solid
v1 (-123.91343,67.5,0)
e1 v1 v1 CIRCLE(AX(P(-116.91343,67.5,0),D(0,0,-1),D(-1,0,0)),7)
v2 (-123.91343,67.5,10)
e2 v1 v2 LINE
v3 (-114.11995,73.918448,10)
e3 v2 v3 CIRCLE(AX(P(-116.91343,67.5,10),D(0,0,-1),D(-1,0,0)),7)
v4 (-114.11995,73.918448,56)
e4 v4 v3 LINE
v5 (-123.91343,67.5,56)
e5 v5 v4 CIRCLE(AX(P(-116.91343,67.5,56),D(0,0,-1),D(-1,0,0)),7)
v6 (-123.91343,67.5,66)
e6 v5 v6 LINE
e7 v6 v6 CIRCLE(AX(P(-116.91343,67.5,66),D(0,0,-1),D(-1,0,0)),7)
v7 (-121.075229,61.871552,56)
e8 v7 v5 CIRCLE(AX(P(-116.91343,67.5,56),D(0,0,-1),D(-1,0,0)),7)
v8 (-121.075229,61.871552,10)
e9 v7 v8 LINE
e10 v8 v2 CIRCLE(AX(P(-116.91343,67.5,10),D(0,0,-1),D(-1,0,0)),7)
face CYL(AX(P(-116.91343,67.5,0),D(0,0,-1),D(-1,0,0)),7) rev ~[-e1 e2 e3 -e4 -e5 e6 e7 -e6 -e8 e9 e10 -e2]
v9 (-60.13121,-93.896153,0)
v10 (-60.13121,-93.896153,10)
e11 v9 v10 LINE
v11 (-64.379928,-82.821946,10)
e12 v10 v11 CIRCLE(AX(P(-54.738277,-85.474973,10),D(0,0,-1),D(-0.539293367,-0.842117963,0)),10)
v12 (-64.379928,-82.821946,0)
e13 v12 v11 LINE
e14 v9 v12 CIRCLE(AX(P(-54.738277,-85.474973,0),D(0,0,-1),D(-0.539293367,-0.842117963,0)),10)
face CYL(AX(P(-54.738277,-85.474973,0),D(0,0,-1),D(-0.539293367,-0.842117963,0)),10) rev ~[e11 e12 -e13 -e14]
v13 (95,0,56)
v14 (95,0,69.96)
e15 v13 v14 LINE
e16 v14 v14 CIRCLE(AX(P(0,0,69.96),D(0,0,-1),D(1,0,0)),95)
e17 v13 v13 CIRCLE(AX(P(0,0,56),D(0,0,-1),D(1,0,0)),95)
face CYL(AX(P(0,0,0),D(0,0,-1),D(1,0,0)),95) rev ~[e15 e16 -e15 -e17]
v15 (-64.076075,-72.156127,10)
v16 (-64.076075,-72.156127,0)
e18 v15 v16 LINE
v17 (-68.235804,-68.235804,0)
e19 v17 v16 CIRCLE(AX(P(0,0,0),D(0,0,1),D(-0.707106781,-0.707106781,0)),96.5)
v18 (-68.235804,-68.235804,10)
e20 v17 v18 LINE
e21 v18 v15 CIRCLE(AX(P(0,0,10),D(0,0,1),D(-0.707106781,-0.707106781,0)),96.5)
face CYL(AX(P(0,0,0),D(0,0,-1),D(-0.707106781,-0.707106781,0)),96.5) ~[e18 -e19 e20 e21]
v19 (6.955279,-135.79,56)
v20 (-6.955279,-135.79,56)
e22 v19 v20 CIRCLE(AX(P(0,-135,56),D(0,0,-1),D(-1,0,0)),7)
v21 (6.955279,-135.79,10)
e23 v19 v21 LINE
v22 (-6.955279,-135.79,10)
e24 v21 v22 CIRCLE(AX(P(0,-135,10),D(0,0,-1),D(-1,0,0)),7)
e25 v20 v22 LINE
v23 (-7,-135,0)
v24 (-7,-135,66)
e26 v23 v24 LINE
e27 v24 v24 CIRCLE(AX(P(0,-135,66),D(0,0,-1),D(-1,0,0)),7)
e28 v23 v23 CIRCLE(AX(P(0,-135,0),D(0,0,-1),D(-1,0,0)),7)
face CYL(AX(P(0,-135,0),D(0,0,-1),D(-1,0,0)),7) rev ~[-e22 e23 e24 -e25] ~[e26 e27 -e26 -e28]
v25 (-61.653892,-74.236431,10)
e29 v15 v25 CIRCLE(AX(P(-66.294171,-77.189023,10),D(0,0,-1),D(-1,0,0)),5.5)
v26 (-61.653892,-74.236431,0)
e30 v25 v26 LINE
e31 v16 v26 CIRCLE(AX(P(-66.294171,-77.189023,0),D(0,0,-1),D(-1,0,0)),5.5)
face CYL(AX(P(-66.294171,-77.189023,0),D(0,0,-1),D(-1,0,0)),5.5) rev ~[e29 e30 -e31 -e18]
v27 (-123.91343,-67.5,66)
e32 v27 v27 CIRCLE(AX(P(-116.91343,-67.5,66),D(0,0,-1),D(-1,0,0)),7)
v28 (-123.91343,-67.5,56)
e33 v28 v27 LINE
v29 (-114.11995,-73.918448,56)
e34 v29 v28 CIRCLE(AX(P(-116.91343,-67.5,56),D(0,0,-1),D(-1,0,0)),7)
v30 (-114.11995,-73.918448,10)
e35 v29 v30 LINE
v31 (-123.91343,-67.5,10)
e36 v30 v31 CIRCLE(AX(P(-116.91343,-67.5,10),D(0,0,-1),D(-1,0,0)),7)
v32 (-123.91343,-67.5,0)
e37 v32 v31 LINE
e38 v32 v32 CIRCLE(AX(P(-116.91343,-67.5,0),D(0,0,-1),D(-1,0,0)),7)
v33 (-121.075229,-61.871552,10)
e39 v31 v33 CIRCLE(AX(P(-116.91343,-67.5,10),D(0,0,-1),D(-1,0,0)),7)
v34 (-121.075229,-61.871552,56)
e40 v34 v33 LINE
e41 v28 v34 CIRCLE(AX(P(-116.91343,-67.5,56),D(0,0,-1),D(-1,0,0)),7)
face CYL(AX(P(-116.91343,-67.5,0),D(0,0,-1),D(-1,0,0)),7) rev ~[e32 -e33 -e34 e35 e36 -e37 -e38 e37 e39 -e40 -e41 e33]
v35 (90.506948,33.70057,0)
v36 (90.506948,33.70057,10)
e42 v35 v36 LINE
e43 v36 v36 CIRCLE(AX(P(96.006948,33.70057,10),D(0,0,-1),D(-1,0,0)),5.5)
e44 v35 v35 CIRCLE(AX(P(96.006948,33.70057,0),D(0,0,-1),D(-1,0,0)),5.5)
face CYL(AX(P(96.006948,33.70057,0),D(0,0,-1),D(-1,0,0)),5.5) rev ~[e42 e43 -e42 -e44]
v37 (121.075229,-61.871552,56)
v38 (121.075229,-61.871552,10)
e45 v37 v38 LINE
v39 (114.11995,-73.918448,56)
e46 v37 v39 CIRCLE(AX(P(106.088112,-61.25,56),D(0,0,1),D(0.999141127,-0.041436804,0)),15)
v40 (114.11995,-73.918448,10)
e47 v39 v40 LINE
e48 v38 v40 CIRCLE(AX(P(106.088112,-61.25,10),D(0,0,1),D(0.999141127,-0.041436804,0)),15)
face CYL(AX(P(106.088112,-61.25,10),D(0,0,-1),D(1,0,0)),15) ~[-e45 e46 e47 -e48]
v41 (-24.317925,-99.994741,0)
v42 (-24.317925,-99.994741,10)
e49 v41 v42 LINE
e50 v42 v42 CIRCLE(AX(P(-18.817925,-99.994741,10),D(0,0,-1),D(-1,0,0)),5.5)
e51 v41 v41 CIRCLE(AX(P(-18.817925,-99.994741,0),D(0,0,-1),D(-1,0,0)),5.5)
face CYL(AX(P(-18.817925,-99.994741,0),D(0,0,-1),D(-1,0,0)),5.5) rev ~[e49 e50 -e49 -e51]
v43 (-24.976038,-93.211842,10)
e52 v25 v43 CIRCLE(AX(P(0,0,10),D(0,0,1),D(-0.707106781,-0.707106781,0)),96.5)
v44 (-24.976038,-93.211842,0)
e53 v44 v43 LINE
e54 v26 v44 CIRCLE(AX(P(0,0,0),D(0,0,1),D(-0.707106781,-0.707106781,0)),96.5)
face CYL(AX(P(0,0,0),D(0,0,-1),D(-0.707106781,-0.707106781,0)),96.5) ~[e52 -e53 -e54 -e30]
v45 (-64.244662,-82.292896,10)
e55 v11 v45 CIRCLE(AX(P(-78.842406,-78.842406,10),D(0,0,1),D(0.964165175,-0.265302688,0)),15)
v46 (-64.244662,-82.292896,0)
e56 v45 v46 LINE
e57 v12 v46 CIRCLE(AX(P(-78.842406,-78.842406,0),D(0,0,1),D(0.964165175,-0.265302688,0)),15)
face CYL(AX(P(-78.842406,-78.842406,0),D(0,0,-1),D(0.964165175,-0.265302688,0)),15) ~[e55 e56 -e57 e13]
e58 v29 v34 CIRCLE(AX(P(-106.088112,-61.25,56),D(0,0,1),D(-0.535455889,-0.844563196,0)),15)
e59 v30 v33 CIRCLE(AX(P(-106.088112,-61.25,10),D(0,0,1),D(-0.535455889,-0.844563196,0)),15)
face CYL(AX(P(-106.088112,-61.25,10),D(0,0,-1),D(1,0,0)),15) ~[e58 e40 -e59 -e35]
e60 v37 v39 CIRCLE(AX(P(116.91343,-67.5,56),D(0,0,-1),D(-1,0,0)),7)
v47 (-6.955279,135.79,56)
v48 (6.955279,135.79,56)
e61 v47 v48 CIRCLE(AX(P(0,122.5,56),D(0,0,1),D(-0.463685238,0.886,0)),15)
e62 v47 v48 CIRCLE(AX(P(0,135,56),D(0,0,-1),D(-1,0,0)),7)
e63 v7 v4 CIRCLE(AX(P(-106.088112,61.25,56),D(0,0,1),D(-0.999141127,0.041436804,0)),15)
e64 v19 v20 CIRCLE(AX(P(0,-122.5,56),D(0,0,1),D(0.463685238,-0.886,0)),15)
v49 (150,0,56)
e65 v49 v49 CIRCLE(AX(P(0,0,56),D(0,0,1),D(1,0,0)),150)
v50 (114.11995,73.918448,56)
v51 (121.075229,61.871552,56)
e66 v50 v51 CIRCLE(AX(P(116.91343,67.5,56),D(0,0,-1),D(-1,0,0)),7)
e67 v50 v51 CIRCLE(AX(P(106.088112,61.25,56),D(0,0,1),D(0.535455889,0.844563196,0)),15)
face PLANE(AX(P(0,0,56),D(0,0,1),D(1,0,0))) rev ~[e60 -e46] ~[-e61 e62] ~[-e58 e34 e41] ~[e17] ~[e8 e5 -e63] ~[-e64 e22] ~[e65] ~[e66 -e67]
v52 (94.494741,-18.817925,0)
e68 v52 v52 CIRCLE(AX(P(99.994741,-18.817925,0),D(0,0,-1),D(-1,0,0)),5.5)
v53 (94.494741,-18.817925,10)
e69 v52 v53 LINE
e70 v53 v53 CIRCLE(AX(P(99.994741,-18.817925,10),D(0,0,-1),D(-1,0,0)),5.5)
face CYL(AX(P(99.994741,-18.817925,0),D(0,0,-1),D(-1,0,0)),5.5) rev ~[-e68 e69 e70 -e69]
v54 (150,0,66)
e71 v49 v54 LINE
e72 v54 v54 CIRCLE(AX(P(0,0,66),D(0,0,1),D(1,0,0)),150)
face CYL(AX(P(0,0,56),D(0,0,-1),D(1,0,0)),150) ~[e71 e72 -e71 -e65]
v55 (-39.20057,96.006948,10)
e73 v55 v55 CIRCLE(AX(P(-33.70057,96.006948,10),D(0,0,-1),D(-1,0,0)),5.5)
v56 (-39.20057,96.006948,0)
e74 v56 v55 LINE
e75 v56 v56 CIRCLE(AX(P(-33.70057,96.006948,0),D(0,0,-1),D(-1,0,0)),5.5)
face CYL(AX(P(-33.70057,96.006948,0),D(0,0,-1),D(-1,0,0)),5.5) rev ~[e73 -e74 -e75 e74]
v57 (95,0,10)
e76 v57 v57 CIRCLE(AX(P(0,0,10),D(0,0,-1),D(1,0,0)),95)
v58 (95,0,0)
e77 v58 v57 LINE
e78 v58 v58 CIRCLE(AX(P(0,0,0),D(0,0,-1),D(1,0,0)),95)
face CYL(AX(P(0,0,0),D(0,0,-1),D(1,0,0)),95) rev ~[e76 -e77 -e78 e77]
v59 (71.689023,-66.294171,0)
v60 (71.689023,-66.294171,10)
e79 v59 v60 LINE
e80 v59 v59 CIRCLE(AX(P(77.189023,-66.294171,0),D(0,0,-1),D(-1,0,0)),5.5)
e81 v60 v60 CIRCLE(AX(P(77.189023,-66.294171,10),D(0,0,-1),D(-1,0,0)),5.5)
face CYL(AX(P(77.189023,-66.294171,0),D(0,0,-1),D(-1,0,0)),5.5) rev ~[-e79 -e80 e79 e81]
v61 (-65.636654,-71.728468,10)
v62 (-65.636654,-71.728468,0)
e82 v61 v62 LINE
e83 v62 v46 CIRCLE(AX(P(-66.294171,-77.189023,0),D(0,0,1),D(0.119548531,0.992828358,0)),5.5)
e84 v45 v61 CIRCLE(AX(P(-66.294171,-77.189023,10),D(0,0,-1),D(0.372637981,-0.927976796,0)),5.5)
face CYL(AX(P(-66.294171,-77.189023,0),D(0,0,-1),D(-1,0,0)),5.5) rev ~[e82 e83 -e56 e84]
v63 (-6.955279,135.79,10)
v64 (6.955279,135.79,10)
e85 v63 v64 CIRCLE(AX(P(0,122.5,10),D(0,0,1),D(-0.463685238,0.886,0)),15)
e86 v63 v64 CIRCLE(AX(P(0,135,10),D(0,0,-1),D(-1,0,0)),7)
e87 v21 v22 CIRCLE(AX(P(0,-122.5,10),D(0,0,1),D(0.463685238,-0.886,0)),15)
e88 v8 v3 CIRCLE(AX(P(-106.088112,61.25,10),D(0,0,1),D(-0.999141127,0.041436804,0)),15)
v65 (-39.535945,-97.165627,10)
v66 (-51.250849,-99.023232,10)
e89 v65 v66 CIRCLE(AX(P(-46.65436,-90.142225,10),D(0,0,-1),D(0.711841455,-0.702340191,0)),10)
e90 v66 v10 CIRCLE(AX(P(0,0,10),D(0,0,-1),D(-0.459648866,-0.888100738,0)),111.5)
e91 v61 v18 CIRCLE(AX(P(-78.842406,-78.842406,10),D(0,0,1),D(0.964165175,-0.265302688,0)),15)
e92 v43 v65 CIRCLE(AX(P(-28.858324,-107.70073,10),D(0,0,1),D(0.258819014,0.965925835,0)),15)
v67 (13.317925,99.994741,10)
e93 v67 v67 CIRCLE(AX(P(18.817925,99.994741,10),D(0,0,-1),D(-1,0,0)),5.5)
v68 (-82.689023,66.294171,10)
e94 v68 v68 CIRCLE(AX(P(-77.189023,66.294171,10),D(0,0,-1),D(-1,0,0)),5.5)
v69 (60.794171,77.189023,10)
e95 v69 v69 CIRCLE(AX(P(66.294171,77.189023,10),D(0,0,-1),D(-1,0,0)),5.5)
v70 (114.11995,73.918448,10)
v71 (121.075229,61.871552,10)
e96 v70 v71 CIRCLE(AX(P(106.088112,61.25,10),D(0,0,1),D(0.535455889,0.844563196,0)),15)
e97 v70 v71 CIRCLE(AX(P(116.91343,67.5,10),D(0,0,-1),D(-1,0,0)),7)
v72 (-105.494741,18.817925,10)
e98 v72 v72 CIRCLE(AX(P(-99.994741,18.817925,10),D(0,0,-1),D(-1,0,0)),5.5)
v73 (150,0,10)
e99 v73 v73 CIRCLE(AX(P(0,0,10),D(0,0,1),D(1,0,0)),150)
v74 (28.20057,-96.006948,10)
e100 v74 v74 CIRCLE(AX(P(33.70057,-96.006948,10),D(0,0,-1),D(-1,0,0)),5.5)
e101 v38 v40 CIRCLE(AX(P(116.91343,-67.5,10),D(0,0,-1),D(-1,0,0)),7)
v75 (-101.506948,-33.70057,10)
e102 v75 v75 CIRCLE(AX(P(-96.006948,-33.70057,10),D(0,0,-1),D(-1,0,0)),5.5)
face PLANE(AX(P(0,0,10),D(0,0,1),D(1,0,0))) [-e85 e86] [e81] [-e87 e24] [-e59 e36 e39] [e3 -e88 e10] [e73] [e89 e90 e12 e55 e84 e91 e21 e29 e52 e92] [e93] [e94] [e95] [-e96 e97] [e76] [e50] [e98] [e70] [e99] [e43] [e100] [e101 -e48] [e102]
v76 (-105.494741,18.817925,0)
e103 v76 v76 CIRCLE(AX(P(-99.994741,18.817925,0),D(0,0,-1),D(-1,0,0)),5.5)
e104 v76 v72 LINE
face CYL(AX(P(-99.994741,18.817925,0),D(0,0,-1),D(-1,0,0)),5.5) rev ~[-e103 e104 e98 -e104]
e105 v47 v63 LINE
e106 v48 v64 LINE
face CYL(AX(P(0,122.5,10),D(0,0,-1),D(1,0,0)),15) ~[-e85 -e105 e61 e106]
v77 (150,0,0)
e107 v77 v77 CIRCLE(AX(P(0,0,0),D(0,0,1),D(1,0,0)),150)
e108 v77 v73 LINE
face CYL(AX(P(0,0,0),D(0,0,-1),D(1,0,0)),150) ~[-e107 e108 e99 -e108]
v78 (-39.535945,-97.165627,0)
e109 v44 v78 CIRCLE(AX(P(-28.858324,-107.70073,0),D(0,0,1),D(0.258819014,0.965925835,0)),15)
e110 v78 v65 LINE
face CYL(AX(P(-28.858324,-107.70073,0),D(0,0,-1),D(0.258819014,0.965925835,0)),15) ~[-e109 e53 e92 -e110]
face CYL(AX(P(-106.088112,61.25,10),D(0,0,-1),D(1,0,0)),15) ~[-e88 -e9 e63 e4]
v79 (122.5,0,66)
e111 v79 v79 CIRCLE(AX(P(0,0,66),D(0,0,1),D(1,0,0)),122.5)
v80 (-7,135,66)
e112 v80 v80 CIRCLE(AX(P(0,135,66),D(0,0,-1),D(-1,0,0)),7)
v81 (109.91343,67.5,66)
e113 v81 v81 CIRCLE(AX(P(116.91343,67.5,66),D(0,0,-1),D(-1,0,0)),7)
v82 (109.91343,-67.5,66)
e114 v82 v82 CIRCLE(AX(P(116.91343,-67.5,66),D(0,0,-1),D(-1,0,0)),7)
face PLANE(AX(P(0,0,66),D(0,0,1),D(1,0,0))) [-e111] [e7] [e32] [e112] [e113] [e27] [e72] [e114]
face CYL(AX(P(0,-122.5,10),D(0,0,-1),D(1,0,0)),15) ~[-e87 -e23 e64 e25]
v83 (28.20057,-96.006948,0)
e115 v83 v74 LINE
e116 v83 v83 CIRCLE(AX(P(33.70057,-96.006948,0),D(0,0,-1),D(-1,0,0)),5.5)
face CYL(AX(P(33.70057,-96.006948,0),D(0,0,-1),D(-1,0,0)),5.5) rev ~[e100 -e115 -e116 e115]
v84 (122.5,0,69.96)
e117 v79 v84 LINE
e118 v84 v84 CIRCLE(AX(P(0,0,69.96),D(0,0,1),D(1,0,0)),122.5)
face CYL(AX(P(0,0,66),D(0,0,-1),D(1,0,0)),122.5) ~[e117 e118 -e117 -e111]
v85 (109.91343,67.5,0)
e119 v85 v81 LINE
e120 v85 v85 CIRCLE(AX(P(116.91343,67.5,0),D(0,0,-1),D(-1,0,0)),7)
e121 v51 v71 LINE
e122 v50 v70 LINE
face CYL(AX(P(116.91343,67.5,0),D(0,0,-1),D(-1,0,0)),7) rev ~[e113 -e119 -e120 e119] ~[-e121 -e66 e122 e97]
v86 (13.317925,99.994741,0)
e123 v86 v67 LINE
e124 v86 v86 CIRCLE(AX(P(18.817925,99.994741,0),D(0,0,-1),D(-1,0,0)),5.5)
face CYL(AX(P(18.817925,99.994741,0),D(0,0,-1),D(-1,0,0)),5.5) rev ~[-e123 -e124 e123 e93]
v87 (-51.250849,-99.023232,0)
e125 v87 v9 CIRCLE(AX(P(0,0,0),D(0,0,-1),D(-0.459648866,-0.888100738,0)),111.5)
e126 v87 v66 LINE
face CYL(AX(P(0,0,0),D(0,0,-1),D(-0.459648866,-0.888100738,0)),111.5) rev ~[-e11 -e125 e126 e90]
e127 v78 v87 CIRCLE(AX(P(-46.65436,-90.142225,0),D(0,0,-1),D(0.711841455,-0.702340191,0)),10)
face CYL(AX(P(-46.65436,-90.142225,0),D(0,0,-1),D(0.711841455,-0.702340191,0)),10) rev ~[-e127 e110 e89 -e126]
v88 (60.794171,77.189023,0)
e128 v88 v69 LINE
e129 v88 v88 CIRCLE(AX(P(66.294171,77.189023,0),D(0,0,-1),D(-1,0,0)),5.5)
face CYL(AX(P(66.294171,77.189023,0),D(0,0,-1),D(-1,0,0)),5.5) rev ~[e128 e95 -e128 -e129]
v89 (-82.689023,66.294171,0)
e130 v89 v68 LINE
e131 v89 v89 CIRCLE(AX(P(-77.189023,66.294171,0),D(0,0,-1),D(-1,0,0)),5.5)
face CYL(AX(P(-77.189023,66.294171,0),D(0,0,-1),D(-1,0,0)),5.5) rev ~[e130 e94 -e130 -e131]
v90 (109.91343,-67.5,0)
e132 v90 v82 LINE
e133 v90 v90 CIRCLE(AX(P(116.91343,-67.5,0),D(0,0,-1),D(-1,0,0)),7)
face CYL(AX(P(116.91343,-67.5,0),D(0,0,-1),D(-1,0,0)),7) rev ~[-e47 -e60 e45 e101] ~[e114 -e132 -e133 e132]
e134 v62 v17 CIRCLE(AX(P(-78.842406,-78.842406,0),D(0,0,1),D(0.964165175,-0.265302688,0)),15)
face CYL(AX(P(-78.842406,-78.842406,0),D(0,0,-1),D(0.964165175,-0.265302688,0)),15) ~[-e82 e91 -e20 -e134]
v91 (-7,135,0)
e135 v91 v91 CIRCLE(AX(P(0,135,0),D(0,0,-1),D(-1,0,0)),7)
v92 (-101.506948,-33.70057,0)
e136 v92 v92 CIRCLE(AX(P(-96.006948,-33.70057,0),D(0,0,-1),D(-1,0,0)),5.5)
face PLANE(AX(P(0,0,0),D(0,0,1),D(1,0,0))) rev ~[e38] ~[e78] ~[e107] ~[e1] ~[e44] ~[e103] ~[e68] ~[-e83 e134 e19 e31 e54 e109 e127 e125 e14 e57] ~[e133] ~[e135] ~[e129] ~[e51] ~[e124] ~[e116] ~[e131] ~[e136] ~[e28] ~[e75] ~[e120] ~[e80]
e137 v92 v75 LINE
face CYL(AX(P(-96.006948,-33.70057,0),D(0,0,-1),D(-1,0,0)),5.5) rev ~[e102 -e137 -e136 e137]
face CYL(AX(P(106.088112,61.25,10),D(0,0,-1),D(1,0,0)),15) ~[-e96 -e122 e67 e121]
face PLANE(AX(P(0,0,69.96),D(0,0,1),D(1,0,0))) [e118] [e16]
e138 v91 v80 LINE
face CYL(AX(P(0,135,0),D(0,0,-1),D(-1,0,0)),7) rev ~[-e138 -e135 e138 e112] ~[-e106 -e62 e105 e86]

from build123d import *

# Parameters (mm, degrees)
SKETCH1_R           = 150
BOSS_EXTRUDE1_DEPTH = 10
SKETCH2_R           = 15
BOSS_EXTRUDE2_DEPTH = 46
SKETCH3_R           = 150
BOSS_EXTRUDE3_DEPTH = 10
SKETCH4_R           = 122.5
BOSS_EXTRUDE4_DEPTH = 3.96
CUT_EXTRUDE2_REACH  = 225.371
SKETCH5_R           = 7
CUT_EXTRUDE3_REACH  = 225.371
SKETCH6_R           = 95
CUT_EXTRUDE9_DEPTH  = 10
SKETCH8_R           = 5.5
CUT_EXTRUDE10_DEPTH = 10


with BuildPart() as part:
    # Sketch1 → Boss-Extrude1 (new body)
    with BuildSketch(Plane.XY):
        Circle(SKETCH1_R)
    extrude(amount=BOSS_EXTRUDE1_DEPTH)

    # Sketch2 → Boss-Extrude2 (add)
    with BuildSketch(Plane.XY.offset(10)):
        with Locations((0, 122.5)):
            Circle(SKETCH2_R)
        with Locations((106.088111964, 61.25)):
            Circle(SKETCH2_R)
        with Locations((106.088111964, -61.25)):
            Circle(SKETCH2_R)
        with Locations((0, -122.5)):
            Circle(SKETCH2_R)
        with Locations((-106.088111964, -61.25)):
            Circle(SKETCH2_R)
        with Locations((-106.088111964, 61.25)):
            Circle(SKETCH2_R)
    extrude(amount=BOSS_EXTRUDE2_DEPTH)

    # Sketch3 → Boss-Extrude3 (add)
    with BuildSketch(Plane.XY.offset(56)):
        Circle(SKETCH3_R)
    extrude(amount=BOSS_EXTRUDE3_DEPTH)

    # Sketch4 → Boss-Extrude4 (add)
    with BuildSketch(Plane.XY.offset(66)):
        Circle(SKETCH4_R)
    extrude(amount=BOSS_EXTRUDE4_DEPTH)

    # Cut-Extrude2: up to this face of the body (flat: up to its plane)
    cut_extrude2_end = Plane(part.part.faces().sort_by_distance((0, 0, 69.96))[0])
    # Sketch5 → Cut-Extrude2 (cut, up to the picked face)
    with BuildSketch(Plane(origin=(0, 0, 0), x_dir=(-1, 0, 0), z_dir=(0, 0, -1)), mode=Mode.PRIVATE) as cut_extrude2_sk1:
        with Locations((0, 135)):
            Circle(SKETCH5_R)
    cut_extrude2_tool1 = split(extrude(cut_extrude2_sk1.sketch, amount=-CUT_EXTRUDE2_REACH, mode=Mode.PRIVATE), bisect_by=cut_extrude2_end, keep=Keep.BOTH, mode=Mode.PRIVATE)
    # Sketch5 → Cut-Extrude2 (cut, up to the picked face)
    with BuildSketch(Plane(origin=(0, 0, 0), x_dir=(-1, 0, 0), z_dir=(0, 0, -1)), mode=Mode.PRIVATE) as cut_extrude2_sk2:
        with Locations((116.913429511, 67.5)):
            Circle(SKETCH5_R)
    cut_extrude2_tool2 = split(extrude(cut_extrude2_sk2.sketch, amount=-CUT_EXTRUDE2_REACH, mode=Mode.PRIVATE), bisect_by=cut_extrude2_end, keep=Keep.BOTH, mode=Mode.PRIVATE)
    # Sketch5 → Cut-Extrude2 (cut, up to the picked face)
    with BuildSketch(Plane(origin=(0, 0, 0), x_dir=(-1, 0, 0), z_dir=(0, 0, -1)), mode=Mode.PRIVATE) as cut_extrude2_sk3:
        with Locations((116.913429511, -67.5)):
            Circle(SKETCH5_R)
    cut_extrude2_tool3 = split(extrude(cut_extrude2_sk3.sketch, amount=-CUT_EXTRUDE2_REACH, mode=Mode.PRIVATE), bisect_by=cut_extrude2_end, keep=Keep.BOTH, mode=Mode.PRIVATE)
    # Sketch5 → Cut-Extrude2 (cut, up to the picked face)
    with BuildSketch(Plane(origin=(0, 0, 0), x_dir=(-1, 0, 0), z_dir=(0, 0, -1)), mode=Mode.PRIVATE) as cut_extrude2_sk4:
        with Locations((0, -135)):
            Circle(SKETCH5_R)
    cut_extrude2_tool4 = split(extrude(cut_extrude2_sk4.sketch, amount=-CUT_EXTRUDE2_REACH, mode=Mode.PRIVATE), bisect_by=cut_extrude2_end, keep=Keep.BOTH, mode=Mode.PRIVATE)
    # Sketch5 → Cut-Extrude2 (cut, up to the picked face)
    with BuildSketch(Plane(origin=(0, 0, 0), x_dir=(-1, 0, 0), z_dir=(0, 0, -1)), mode=Mode.PRIVATE) as cut_extrude2_sk5:
        with Locations((-116.913429511, -67.5)):
            Circle(SKETCH5_R)
    cut_extrude2_tool5 = split(extrude(cut_extrude2_sk5.sketch, amount=-CUT_EXTRUDE2_REACH, mode=Mode.PRIVATE), bisect_by=cut_extrude2_end, keep=Keep.BOTH, mode=Mode.PRIVATE)
    # Sketch5 → Cut-Extrude2 (cut, up to the picked face)
    with BuildSketch(Plane(origin=(0, 0, 0), x_dir=(-1, 0, 0), z_dir=(0, 0, -1)), mode=Mode.PRIVATE) as cut_extrude2_sk6:
        with Locations((-116.913429511, 67.5)):
            Circle(SKETCH5_R)
    cut_extrude2_tool6 = split(extrude(cut_extrude2_sk6.sketch, amount=-CUT_EXTRUDE2_REACH, mode=Mode.PRIVATE), bisect_by=cut_extrude2_end, keep=Keep.BOTH, mode=Mode.PRIVATE)
    add(cut_extrude2_tool1.solids().sort_by(Axis((0, 135, 0), (0, 0, 1)))[0], mode=Mode.SUBTRACT)
    add(cut_extrude2_tool2.solids().sort_by(Axis((-116.91343, 67.5, 0), (0, 0, 1)))[0], mode=Mode.SUBTRACT)
    add(cut_extrude2_tool3.solids().sort_by(Axis((-116.91343, -67.5, 0), (0, 0, 1)))[0], mode=Mode.SUBTRACT)
    add(cut_extrude2_tool4.solids().sort_by(Axis((0, -135, 0), (0, 0, 1)))[0], mode=Mode.SUBTRACT)
    add(cut_extrude2_tool5.solids().sort_by(Axis((116.91343, -67.5, 0), (0, 0, 1)))[0], mode=Mode.SUBTRACT)
    add(cut_extrude2_tool6.solids().sort_by(Axis((116.91343, 67.5, 0), (0, 0, 1)))[0], mode=Mode.SUBTRACT)

    # Cut-Extrude3: up to this face of the body (flat: up to its plane)
    cut_extrude3_end = Plane(part.part.faces().sort_by_distance((0, 0, 69.96))[0])
    # Sketch6 → Cut-Extrude3 (cut, up to the picked face)
    with BuildSketch(Plane(origin=(0, 0, 0), x_dir=(-1, 0, 0), z_dir=(0, 0, -1)), mode=Mode.PRIVATE) as cut_extrude3_sk1:
        with Locations(Location((0, 0, 0), (0, 0, 180))):
            Circle(SKETCH6_R)
    cut_extrude3_tool1 = split(extrude(cut_extrude3_sk1.sketch, amount=-CUT_EXTRUDE3_REACH, mode=Mode.PRIVATE), bisect_by=cut_extrude3_end, keep=Keep.BOTH, mode=Mode.PRIVATE)
    add(cut_extrude3_tool1.solids().sort_by(Axis((0, 0, 0), (0, 0, 1)))[0], mode=Mode.SUBTRACT)

    # Sketch7 → Cut-Extrude9 (cut)
    with BuildSketch(Plane(origin=(0, 0, 0), x_dir=(-1, 0, 0), z_dir=(0, 0, -1))):
        with BuildLine():
            ThreePointArc((68.235804385, -68.235804384), (48.250000208, -83.571451345), (24.976038317, -93.211842112))
            ThreePointArc((24.976038317, -93.211842112), (32.789258936, -93.224965512), (39.535945347, -97.165626769))
            ThreePointArc((39.535945347, -97.165626769), (45.088249404, -100.018828425), (51.250848552, -99.023232237))
            ThreePointArc((51.250848552, -99.023232237), (55.75, -96.561832522), (60.131210406, -93.89615293))
            ThreePointArc((60.131210406, -93.89615293), (64.07472157, -89.056983608), (64.379928483, -82.821946418))
            ThreePointArc((64.379928483, -82.821946418), (64.340558994, -75.008813734), (68.235804385, -68.235804384))
        make_face()
    extrude(amount=-CUT_EXTRUDE9_DEPTH, mode=Mode.SUBTRACT)

    # Sketch8 → Cut-Extrude10 (cut)
    with BuildSketch(Plane(origin=(0, 0, 0), x_dir=(-1, 0, 0), z_dir=(0, 0, -1))):
        with Locations((18.817924745, -99.994740903)):
            Circle(SKETCH8_R)
        with Locations((-33.700569576, -96.00694824)):
            Circle(SKETCH8_R)
        with Locations((-77.189023494, -66.294171327)):
            Circle(SKETCH8_R)
        with Locations((-99.994740903, -18.817924745)):
            Circle(SKETCH8_R)
        with Locations((-96.00694824, 33.700569576)):
            Circle(SKETCH8_R)
        with Locations((-66.294171327, 77.189023494)):
            Circle(SKETCH8_R)
        with Locations((-18.817924745, 99.994740903)):
            Circle(SKETCH8_R)
        with Locations((33.700569576, 96.00694824)):
            Circle(SKETCH8_R)
        with Locations((77.189023494, 66.294171327)):
            Circle(SKETCH8_R)
        with Locations((99.994740903, 18.817924745)):
            Circle(SKETCH8_R)
        with Locations((96.00694824, -33.700569576)):
            Circle(SKETCH8_R)
        with Locations((66.294171327, -77.189023494)):
            Circle(SKETCH8_R)
    extrude(amount=-CUT_EXTRUDE10_DEPTH, mode=Mode.SUBTRACT)


solid = part.part
